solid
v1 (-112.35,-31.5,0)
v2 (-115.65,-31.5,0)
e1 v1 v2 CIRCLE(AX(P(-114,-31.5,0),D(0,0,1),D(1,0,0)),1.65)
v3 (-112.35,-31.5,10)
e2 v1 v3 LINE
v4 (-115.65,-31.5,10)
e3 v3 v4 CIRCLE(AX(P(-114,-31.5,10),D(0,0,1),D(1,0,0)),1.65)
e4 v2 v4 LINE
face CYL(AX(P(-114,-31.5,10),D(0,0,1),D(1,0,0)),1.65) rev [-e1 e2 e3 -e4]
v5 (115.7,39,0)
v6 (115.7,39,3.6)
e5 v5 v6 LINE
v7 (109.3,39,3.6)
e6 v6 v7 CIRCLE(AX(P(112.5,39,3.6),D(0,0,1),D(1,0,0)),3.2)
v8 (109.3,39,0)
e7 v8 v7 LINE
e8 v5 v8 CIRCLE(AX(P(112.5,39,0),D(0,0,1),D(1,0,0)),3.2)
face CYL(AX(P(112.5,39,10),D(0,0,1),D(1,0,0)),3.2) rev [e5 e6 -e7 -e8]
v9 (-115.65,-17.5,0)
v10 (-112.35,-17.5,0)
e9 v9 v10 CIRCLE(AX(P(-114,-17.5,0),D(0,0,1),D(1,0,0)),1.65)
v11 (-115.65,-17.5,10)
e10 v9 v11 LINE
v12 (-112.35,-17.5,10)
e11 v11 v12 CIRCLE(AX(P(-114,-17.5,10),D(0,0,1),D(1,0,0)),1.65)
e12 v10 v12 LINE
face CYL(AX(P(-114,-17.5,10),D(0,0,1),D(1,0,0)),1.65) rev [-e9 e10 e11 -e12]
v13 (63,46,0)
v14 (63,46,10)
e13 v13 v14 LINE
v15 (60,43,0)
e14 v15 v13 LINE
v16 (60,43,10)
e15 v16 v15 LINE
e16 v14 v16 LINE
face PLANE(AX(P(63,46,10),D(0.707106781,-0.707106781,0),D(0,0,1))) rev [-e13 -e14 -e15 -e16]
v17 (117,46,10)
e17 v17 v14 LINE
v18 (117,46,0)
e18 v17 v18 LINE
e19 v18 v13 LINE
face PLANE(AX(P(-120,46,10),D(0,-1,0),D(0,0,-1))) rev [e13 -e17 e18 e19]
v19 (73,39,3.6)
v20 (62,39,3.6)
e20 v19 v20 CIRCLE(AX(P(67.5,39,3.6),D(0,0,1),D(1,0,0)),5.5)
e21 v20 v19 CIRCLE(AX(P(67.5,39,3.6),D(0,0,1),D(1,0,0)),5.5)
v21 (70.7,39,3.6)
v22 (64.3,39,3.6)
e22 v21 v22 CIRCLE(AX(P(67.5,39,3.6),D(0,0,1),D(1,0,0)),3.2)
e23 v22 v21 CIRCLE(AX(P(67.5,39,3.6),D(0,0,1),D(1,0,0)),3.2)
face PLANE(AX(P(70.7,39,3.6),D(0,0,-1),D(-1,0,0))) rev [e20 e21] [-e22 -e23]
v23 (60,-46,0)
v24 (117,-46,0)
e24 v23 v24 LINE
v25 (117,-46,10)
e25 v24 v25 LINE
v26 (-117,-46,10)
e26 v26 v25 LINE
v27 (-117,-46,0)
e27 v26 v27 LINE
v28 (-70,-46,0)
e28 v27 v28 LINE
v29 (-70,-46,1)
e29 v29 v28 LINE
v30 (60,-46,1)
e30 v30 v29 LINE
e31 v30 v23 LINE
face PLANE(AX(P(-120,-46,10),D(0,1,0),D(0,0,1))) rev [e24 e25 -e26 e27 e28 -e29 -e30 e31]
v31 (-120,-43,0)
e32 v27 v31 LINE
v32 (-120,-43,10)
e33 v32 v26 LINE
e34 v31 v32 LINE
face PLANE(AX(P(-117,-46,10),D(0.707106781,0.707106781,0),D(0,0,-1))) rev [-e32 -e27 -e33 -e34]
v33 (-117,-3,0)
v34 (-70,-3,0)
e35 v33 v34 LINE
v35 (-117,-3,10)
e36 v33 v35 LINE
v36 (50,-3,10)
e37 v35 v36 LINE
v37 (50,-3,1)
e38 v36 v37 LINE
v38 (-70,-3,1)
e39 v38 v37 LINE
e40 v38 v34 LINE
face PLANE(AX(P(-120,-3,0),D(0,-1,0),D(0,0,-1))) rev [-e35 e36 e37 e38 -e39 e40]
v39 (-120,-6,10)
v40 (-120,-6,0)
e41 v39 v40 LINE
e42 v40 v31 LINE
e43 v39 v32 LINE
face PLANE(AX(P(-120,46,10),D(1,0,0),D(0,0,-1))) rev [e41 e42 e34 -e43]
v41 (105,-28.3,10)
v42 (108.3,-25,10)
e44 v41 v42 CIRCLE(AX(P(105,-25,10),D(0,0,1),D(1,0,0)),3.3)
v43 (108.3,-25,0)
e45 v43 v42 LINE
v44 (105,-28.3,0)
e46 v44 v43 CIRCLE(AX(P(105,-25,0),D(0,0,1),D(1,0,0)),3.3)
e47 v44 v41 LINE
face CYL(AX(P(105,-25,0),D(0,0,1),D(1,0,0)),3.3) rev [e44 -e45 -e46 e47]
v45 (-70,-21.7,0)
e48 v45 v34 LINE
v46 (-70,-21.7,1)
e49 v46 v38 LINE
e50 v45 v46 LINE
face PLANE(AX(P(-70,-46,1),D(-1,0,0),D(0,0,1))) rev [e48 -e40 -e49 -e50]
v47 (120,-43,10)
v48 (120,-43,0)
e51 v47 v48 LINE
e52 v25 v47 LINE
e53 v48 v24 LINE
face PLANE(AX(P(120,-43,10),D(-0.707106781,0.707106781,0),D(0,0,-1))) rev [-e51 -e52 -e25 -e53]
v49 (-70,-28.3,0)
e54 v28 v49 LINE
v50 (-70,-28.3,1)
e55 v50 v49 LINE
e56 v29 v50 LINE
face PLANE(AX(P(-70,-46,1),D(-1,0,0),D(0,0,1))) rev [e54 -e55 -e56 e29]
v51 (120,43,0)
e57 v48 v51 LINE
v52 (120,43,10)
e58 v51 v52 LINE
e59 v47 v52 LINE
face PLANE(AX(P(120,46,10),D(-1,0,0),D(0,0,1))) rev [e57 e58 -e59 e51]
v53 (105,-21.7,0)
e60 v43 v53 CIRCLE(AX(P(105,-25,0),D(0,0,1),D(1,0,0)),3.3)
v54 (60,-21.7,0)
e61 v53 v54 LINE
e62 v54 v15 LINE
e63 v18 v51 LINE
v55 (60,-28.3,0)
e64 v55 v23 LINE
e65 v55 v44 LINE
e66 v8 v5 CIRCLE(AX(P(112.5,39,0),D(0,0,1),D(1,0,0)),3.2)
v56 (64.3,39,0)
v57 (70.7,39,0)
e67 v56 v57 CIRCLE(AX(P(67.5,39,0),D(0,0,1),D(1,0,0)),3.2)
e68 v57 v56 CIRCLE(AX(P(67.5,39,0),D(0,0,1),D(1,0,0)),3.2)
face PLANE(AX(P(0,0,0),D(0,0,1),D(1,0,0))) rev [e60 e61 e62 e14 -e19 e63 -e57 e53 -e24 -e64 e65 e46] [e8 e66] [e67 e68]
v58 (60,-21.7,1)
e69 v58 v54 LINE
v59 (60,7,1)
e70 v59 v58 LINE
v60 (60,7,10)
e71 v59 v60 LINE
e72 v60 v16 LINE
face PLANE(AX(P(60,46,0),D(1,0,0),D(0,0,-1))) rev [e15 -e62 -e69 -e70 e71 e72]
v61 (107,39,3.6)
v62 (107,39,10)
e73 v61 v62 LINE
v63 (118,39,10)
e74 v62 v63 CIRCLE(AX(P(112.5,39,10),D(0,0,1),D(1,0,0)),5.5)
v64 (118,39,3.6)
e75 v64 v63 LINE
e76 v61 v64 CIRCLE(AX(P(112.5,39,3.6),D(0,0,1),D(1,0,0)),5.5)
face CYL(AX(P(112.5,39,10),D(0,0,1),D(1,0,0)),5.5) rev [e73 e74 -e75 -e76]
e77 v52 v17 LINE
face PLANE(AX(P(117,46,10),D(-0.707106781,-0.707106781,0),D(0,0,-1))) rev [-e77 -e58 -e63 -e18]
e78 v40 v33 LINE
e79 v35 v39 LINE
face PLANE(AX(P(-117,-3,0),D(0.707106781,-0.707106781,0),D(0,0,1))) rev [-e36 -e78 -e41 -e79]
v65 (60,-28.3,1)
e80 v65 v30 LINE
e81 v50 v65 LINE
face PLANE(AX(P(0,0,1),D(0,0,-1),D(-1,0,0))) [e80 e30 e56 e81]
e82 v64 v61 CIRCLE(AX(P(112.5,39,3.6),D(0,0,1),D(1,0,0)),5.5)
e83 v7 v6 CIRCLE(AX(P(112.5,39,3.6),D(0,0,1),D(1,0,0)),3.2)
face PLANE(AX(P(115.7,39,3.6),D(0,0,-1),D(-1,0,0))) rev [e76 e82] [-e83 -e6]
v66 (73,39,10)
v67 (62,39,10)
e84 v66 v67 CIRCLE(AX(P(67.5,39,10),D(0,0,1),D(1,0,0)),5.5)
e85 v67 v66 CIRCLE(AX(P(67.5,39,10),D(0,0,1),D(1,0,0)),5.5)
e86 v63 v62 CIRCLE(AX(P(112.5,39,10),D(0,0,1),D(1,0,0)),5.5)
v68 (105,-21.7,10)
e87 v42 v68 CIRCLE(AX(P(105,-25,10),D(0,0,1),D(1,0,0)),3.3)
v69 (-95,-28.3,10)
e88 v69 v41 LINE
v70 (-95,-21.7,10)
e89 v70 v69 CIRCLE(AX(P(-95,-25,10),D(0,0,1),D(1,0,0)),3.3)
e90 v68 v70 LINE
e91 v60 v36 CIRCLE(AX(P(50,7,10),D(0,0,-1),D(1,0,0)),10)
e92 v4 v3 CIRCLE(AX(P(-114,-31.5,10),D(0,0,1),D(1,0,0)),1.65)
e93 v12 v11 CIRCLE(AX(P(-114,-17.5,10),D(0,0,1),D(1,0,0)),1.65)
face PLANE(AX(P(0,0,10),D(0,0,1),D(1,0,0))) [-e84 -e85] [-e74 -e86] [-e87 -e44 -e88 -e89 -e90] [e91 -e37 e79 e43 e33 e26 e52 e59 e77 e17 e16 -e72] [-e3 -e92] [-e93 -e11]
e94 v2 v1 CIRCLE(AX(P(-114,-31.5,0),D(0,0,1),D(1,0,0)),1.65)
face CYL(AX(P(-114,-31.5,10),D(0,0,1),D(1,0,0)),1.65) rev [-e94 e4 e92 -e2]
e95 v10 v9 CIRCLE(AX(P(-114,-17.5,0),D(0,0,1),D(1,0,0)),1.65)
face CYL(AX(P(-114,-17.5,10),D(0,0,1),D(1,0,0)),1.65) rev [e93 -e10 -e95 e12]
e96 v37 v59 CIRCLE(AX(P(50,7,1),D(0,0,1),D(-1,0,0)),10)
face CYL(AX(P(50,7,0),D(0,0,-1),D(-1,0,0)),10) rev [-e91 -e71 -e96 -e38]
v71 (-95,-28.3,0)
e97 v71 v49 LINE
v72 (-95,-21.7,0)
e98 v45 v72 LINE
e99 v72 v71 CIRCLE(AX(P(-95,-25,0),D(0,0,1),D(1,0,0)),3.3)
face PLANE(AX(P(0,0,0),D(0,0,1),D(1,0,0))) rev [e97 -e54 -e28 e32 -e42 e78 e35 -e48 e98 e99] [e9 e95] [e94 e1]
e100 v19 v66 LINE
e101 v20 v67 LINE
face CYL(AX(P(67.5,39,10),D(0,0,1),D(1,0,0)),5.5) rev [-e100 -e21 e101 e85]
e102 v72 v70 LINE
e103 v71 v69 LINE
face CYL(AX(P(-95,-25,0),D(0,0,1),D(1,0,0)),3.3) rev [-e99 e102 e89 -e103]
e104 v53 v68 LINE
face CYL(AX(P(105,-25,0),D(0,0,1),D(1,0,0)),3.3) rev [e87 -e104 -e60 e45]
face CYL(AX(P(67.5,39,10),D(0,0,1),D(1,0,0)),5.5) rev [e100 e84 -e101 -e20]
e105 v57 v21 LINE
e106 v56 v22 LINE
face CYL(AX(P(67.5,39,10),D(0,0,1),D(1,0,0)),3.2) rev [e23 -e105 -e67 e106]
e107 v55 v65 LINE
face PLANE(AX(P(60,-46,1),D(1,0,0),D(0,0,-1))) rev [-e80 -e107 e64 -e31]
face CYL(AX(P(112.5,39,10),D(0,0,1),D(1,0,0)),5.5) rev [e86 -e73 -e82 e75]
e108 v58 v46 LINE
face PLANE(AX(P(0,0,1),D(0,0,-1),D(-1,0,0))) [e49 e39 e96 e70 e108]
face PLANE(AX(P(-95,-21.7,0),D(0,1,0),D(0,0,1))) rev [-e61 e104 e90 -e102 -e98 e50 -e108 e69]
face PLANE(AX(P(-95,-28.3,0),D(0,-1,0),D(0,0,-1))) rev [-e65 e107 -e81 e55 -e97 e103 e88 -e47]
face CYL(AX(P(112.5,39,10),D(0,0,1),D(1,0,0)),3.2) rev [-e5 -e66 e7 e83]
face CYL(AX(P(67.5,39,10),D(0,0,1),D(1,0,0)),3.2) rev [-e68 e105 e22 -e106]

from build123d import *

# Parameters (mm, degrees)
SKETCH1_W                                           = 240
SKETCH1_H                                           = 92
BOSS_EXTRUDE1_DEPTH                                 = 10
CUT_EXTRUDE1_DEPTH                                  = 10
SKETCH3_W                                           = 180
SKETCH3_H                                           = 49
CUT_EXTRUDE2_DEPTH                                  = 10
FILLET1_R                                           = 10
CHAMFER1_SIZE                                       = 3
M4_TAPPED_HOLE1_D                                   = 3.3
M4_TAPPED_HOLE1_DEPTH                               = 11.5
M4_TAPPED_HOLE1_TIP                                 = 0.991420021
CBORE_FOR_M6_HEX_SOCKET_HEAD_CAP_SCREW1_D           = 6.4
CBORE_FOR_M6_HEX_SOCKET_HEAD_CAP_SCREW1_CBORE_D     = 11
CBORE_FOR_M6_HEX_SOCKET_HEAD_CAP_SCREW1_CBORE_DEPTH = 6.4
SKETCH8_W                                           = 130
SKETCH8_H                                           = 89
CUT_EXTRUDE3_DEPTH                                  = 1


with BuildPart() as part:
    # Sketch1 → Boss-Extrude1 (new body)
    with BuildSketch(Plane.XY):
        Rectangle(SKETCH1_W, SKETCH1_H)
    extrude(amount=BOSS_EXTRUDE1_DEPTH)

    # Sketch2 → Cut-Extrude1 (cut)
    with BuildSketch(Plane.XY.offset(10)):
        with BuildLine():
            Line((-95, -21.7), (105, -21.7))
            ThreePointArc((105, -21.7), (108.3, -25), (105, -28.3))
            Line((105, -28.3), (-95, -28.3))
            ThreePointArc((-95, -28.3), (-98.3, -25), (-95, -21.7))
        make_face()
    extrude(amount=-CUT_EXTRUDE1_DEPTH, mode=Mode.SUBTRACT)

    # Sketch3 → Cut-Extrude2 (cut)
    with BuildSketch(Plane.XY.offset(10)):
        with Locations((-30, 21.5)):
            Rectangle(SKETCH3_W, SKETCH3_H)
    extrude(amount=-CUT_EXTRUDE2_DEPTH, mode=Mode.SUBTRACT)

    # Fillet1
    fillet1_edges = [part.edges().sort_by_distance(p)[0] for p in [
        (60, -3, 5),
    ]]
    fillet(fillet1_edges, radius=FILLET1_R)

    # Chamfer1
    chamfer1_edges = [part.edges().sort_by_distance(p)[0] for p in [
        (-120, -3, 5),
        (60, 46, 5),
        (120, -46, 5),
        (-120, -46, 5),
        (120, 46, 5),
    ]]
    chamfer(chamfer1_edges, length=CHAMFER1_SIZE)

    # M4 Tapped Hole1
    with Locations(Plane.XY.offset(10)):
        with Locations((-114, -17.5), (-114, -31.5)):
            Hole(M4_TAPPED_HOLE1_D / 2, depth=M4_TAPPED_HOLE1_DEPTH)
            with Locations((0, 0, -(M4_TAPPED_HOLE1_DEPTH + M4_TAPPED_HOLE1_TIP / 2))):  # 118° drill point
                Cone(0, M4_TAPPED_HOLE1_D / 2, M4_TAPPED_HOLE1_TIP, mode=Mode.SUBTRACT)

    # CBORE for M6 Hex Socket Head Cap Screw1 (through all)
    with Locations(Plane.XY.offset(10)):
        with Locations((67.5, 39), (112.5, 39)):
            CounterBoreHole(CBORE_FOR_M6_HEX_SOCKET_HEAD_CAP_SCREW1_D / 2, CBORE_FOR_M6_HEX_SOCKET_HEAD_CAP_SCREW1_CBORE_D / 2, CBORE_FOR_M6_HEX_SOCKET_HEAD_CAP_SCREW1_CBORE_DEPTH)

    # Sketch8 → Cut-Extrude3 (cut)
    with BuildSketch(Plane(origin=(0, 0, 0), x_dir=(-1, 0, 0), z_dir=(0, 0, -1))):
        with Locations((5, -1.5)):
            Rectangle(SKETCH8_W, SKETCH8_H)
    extrude(amount=-CUT_EXTRUDE3_DEPTH, mode=Mode.SUBTRACT)


solid = part.part
